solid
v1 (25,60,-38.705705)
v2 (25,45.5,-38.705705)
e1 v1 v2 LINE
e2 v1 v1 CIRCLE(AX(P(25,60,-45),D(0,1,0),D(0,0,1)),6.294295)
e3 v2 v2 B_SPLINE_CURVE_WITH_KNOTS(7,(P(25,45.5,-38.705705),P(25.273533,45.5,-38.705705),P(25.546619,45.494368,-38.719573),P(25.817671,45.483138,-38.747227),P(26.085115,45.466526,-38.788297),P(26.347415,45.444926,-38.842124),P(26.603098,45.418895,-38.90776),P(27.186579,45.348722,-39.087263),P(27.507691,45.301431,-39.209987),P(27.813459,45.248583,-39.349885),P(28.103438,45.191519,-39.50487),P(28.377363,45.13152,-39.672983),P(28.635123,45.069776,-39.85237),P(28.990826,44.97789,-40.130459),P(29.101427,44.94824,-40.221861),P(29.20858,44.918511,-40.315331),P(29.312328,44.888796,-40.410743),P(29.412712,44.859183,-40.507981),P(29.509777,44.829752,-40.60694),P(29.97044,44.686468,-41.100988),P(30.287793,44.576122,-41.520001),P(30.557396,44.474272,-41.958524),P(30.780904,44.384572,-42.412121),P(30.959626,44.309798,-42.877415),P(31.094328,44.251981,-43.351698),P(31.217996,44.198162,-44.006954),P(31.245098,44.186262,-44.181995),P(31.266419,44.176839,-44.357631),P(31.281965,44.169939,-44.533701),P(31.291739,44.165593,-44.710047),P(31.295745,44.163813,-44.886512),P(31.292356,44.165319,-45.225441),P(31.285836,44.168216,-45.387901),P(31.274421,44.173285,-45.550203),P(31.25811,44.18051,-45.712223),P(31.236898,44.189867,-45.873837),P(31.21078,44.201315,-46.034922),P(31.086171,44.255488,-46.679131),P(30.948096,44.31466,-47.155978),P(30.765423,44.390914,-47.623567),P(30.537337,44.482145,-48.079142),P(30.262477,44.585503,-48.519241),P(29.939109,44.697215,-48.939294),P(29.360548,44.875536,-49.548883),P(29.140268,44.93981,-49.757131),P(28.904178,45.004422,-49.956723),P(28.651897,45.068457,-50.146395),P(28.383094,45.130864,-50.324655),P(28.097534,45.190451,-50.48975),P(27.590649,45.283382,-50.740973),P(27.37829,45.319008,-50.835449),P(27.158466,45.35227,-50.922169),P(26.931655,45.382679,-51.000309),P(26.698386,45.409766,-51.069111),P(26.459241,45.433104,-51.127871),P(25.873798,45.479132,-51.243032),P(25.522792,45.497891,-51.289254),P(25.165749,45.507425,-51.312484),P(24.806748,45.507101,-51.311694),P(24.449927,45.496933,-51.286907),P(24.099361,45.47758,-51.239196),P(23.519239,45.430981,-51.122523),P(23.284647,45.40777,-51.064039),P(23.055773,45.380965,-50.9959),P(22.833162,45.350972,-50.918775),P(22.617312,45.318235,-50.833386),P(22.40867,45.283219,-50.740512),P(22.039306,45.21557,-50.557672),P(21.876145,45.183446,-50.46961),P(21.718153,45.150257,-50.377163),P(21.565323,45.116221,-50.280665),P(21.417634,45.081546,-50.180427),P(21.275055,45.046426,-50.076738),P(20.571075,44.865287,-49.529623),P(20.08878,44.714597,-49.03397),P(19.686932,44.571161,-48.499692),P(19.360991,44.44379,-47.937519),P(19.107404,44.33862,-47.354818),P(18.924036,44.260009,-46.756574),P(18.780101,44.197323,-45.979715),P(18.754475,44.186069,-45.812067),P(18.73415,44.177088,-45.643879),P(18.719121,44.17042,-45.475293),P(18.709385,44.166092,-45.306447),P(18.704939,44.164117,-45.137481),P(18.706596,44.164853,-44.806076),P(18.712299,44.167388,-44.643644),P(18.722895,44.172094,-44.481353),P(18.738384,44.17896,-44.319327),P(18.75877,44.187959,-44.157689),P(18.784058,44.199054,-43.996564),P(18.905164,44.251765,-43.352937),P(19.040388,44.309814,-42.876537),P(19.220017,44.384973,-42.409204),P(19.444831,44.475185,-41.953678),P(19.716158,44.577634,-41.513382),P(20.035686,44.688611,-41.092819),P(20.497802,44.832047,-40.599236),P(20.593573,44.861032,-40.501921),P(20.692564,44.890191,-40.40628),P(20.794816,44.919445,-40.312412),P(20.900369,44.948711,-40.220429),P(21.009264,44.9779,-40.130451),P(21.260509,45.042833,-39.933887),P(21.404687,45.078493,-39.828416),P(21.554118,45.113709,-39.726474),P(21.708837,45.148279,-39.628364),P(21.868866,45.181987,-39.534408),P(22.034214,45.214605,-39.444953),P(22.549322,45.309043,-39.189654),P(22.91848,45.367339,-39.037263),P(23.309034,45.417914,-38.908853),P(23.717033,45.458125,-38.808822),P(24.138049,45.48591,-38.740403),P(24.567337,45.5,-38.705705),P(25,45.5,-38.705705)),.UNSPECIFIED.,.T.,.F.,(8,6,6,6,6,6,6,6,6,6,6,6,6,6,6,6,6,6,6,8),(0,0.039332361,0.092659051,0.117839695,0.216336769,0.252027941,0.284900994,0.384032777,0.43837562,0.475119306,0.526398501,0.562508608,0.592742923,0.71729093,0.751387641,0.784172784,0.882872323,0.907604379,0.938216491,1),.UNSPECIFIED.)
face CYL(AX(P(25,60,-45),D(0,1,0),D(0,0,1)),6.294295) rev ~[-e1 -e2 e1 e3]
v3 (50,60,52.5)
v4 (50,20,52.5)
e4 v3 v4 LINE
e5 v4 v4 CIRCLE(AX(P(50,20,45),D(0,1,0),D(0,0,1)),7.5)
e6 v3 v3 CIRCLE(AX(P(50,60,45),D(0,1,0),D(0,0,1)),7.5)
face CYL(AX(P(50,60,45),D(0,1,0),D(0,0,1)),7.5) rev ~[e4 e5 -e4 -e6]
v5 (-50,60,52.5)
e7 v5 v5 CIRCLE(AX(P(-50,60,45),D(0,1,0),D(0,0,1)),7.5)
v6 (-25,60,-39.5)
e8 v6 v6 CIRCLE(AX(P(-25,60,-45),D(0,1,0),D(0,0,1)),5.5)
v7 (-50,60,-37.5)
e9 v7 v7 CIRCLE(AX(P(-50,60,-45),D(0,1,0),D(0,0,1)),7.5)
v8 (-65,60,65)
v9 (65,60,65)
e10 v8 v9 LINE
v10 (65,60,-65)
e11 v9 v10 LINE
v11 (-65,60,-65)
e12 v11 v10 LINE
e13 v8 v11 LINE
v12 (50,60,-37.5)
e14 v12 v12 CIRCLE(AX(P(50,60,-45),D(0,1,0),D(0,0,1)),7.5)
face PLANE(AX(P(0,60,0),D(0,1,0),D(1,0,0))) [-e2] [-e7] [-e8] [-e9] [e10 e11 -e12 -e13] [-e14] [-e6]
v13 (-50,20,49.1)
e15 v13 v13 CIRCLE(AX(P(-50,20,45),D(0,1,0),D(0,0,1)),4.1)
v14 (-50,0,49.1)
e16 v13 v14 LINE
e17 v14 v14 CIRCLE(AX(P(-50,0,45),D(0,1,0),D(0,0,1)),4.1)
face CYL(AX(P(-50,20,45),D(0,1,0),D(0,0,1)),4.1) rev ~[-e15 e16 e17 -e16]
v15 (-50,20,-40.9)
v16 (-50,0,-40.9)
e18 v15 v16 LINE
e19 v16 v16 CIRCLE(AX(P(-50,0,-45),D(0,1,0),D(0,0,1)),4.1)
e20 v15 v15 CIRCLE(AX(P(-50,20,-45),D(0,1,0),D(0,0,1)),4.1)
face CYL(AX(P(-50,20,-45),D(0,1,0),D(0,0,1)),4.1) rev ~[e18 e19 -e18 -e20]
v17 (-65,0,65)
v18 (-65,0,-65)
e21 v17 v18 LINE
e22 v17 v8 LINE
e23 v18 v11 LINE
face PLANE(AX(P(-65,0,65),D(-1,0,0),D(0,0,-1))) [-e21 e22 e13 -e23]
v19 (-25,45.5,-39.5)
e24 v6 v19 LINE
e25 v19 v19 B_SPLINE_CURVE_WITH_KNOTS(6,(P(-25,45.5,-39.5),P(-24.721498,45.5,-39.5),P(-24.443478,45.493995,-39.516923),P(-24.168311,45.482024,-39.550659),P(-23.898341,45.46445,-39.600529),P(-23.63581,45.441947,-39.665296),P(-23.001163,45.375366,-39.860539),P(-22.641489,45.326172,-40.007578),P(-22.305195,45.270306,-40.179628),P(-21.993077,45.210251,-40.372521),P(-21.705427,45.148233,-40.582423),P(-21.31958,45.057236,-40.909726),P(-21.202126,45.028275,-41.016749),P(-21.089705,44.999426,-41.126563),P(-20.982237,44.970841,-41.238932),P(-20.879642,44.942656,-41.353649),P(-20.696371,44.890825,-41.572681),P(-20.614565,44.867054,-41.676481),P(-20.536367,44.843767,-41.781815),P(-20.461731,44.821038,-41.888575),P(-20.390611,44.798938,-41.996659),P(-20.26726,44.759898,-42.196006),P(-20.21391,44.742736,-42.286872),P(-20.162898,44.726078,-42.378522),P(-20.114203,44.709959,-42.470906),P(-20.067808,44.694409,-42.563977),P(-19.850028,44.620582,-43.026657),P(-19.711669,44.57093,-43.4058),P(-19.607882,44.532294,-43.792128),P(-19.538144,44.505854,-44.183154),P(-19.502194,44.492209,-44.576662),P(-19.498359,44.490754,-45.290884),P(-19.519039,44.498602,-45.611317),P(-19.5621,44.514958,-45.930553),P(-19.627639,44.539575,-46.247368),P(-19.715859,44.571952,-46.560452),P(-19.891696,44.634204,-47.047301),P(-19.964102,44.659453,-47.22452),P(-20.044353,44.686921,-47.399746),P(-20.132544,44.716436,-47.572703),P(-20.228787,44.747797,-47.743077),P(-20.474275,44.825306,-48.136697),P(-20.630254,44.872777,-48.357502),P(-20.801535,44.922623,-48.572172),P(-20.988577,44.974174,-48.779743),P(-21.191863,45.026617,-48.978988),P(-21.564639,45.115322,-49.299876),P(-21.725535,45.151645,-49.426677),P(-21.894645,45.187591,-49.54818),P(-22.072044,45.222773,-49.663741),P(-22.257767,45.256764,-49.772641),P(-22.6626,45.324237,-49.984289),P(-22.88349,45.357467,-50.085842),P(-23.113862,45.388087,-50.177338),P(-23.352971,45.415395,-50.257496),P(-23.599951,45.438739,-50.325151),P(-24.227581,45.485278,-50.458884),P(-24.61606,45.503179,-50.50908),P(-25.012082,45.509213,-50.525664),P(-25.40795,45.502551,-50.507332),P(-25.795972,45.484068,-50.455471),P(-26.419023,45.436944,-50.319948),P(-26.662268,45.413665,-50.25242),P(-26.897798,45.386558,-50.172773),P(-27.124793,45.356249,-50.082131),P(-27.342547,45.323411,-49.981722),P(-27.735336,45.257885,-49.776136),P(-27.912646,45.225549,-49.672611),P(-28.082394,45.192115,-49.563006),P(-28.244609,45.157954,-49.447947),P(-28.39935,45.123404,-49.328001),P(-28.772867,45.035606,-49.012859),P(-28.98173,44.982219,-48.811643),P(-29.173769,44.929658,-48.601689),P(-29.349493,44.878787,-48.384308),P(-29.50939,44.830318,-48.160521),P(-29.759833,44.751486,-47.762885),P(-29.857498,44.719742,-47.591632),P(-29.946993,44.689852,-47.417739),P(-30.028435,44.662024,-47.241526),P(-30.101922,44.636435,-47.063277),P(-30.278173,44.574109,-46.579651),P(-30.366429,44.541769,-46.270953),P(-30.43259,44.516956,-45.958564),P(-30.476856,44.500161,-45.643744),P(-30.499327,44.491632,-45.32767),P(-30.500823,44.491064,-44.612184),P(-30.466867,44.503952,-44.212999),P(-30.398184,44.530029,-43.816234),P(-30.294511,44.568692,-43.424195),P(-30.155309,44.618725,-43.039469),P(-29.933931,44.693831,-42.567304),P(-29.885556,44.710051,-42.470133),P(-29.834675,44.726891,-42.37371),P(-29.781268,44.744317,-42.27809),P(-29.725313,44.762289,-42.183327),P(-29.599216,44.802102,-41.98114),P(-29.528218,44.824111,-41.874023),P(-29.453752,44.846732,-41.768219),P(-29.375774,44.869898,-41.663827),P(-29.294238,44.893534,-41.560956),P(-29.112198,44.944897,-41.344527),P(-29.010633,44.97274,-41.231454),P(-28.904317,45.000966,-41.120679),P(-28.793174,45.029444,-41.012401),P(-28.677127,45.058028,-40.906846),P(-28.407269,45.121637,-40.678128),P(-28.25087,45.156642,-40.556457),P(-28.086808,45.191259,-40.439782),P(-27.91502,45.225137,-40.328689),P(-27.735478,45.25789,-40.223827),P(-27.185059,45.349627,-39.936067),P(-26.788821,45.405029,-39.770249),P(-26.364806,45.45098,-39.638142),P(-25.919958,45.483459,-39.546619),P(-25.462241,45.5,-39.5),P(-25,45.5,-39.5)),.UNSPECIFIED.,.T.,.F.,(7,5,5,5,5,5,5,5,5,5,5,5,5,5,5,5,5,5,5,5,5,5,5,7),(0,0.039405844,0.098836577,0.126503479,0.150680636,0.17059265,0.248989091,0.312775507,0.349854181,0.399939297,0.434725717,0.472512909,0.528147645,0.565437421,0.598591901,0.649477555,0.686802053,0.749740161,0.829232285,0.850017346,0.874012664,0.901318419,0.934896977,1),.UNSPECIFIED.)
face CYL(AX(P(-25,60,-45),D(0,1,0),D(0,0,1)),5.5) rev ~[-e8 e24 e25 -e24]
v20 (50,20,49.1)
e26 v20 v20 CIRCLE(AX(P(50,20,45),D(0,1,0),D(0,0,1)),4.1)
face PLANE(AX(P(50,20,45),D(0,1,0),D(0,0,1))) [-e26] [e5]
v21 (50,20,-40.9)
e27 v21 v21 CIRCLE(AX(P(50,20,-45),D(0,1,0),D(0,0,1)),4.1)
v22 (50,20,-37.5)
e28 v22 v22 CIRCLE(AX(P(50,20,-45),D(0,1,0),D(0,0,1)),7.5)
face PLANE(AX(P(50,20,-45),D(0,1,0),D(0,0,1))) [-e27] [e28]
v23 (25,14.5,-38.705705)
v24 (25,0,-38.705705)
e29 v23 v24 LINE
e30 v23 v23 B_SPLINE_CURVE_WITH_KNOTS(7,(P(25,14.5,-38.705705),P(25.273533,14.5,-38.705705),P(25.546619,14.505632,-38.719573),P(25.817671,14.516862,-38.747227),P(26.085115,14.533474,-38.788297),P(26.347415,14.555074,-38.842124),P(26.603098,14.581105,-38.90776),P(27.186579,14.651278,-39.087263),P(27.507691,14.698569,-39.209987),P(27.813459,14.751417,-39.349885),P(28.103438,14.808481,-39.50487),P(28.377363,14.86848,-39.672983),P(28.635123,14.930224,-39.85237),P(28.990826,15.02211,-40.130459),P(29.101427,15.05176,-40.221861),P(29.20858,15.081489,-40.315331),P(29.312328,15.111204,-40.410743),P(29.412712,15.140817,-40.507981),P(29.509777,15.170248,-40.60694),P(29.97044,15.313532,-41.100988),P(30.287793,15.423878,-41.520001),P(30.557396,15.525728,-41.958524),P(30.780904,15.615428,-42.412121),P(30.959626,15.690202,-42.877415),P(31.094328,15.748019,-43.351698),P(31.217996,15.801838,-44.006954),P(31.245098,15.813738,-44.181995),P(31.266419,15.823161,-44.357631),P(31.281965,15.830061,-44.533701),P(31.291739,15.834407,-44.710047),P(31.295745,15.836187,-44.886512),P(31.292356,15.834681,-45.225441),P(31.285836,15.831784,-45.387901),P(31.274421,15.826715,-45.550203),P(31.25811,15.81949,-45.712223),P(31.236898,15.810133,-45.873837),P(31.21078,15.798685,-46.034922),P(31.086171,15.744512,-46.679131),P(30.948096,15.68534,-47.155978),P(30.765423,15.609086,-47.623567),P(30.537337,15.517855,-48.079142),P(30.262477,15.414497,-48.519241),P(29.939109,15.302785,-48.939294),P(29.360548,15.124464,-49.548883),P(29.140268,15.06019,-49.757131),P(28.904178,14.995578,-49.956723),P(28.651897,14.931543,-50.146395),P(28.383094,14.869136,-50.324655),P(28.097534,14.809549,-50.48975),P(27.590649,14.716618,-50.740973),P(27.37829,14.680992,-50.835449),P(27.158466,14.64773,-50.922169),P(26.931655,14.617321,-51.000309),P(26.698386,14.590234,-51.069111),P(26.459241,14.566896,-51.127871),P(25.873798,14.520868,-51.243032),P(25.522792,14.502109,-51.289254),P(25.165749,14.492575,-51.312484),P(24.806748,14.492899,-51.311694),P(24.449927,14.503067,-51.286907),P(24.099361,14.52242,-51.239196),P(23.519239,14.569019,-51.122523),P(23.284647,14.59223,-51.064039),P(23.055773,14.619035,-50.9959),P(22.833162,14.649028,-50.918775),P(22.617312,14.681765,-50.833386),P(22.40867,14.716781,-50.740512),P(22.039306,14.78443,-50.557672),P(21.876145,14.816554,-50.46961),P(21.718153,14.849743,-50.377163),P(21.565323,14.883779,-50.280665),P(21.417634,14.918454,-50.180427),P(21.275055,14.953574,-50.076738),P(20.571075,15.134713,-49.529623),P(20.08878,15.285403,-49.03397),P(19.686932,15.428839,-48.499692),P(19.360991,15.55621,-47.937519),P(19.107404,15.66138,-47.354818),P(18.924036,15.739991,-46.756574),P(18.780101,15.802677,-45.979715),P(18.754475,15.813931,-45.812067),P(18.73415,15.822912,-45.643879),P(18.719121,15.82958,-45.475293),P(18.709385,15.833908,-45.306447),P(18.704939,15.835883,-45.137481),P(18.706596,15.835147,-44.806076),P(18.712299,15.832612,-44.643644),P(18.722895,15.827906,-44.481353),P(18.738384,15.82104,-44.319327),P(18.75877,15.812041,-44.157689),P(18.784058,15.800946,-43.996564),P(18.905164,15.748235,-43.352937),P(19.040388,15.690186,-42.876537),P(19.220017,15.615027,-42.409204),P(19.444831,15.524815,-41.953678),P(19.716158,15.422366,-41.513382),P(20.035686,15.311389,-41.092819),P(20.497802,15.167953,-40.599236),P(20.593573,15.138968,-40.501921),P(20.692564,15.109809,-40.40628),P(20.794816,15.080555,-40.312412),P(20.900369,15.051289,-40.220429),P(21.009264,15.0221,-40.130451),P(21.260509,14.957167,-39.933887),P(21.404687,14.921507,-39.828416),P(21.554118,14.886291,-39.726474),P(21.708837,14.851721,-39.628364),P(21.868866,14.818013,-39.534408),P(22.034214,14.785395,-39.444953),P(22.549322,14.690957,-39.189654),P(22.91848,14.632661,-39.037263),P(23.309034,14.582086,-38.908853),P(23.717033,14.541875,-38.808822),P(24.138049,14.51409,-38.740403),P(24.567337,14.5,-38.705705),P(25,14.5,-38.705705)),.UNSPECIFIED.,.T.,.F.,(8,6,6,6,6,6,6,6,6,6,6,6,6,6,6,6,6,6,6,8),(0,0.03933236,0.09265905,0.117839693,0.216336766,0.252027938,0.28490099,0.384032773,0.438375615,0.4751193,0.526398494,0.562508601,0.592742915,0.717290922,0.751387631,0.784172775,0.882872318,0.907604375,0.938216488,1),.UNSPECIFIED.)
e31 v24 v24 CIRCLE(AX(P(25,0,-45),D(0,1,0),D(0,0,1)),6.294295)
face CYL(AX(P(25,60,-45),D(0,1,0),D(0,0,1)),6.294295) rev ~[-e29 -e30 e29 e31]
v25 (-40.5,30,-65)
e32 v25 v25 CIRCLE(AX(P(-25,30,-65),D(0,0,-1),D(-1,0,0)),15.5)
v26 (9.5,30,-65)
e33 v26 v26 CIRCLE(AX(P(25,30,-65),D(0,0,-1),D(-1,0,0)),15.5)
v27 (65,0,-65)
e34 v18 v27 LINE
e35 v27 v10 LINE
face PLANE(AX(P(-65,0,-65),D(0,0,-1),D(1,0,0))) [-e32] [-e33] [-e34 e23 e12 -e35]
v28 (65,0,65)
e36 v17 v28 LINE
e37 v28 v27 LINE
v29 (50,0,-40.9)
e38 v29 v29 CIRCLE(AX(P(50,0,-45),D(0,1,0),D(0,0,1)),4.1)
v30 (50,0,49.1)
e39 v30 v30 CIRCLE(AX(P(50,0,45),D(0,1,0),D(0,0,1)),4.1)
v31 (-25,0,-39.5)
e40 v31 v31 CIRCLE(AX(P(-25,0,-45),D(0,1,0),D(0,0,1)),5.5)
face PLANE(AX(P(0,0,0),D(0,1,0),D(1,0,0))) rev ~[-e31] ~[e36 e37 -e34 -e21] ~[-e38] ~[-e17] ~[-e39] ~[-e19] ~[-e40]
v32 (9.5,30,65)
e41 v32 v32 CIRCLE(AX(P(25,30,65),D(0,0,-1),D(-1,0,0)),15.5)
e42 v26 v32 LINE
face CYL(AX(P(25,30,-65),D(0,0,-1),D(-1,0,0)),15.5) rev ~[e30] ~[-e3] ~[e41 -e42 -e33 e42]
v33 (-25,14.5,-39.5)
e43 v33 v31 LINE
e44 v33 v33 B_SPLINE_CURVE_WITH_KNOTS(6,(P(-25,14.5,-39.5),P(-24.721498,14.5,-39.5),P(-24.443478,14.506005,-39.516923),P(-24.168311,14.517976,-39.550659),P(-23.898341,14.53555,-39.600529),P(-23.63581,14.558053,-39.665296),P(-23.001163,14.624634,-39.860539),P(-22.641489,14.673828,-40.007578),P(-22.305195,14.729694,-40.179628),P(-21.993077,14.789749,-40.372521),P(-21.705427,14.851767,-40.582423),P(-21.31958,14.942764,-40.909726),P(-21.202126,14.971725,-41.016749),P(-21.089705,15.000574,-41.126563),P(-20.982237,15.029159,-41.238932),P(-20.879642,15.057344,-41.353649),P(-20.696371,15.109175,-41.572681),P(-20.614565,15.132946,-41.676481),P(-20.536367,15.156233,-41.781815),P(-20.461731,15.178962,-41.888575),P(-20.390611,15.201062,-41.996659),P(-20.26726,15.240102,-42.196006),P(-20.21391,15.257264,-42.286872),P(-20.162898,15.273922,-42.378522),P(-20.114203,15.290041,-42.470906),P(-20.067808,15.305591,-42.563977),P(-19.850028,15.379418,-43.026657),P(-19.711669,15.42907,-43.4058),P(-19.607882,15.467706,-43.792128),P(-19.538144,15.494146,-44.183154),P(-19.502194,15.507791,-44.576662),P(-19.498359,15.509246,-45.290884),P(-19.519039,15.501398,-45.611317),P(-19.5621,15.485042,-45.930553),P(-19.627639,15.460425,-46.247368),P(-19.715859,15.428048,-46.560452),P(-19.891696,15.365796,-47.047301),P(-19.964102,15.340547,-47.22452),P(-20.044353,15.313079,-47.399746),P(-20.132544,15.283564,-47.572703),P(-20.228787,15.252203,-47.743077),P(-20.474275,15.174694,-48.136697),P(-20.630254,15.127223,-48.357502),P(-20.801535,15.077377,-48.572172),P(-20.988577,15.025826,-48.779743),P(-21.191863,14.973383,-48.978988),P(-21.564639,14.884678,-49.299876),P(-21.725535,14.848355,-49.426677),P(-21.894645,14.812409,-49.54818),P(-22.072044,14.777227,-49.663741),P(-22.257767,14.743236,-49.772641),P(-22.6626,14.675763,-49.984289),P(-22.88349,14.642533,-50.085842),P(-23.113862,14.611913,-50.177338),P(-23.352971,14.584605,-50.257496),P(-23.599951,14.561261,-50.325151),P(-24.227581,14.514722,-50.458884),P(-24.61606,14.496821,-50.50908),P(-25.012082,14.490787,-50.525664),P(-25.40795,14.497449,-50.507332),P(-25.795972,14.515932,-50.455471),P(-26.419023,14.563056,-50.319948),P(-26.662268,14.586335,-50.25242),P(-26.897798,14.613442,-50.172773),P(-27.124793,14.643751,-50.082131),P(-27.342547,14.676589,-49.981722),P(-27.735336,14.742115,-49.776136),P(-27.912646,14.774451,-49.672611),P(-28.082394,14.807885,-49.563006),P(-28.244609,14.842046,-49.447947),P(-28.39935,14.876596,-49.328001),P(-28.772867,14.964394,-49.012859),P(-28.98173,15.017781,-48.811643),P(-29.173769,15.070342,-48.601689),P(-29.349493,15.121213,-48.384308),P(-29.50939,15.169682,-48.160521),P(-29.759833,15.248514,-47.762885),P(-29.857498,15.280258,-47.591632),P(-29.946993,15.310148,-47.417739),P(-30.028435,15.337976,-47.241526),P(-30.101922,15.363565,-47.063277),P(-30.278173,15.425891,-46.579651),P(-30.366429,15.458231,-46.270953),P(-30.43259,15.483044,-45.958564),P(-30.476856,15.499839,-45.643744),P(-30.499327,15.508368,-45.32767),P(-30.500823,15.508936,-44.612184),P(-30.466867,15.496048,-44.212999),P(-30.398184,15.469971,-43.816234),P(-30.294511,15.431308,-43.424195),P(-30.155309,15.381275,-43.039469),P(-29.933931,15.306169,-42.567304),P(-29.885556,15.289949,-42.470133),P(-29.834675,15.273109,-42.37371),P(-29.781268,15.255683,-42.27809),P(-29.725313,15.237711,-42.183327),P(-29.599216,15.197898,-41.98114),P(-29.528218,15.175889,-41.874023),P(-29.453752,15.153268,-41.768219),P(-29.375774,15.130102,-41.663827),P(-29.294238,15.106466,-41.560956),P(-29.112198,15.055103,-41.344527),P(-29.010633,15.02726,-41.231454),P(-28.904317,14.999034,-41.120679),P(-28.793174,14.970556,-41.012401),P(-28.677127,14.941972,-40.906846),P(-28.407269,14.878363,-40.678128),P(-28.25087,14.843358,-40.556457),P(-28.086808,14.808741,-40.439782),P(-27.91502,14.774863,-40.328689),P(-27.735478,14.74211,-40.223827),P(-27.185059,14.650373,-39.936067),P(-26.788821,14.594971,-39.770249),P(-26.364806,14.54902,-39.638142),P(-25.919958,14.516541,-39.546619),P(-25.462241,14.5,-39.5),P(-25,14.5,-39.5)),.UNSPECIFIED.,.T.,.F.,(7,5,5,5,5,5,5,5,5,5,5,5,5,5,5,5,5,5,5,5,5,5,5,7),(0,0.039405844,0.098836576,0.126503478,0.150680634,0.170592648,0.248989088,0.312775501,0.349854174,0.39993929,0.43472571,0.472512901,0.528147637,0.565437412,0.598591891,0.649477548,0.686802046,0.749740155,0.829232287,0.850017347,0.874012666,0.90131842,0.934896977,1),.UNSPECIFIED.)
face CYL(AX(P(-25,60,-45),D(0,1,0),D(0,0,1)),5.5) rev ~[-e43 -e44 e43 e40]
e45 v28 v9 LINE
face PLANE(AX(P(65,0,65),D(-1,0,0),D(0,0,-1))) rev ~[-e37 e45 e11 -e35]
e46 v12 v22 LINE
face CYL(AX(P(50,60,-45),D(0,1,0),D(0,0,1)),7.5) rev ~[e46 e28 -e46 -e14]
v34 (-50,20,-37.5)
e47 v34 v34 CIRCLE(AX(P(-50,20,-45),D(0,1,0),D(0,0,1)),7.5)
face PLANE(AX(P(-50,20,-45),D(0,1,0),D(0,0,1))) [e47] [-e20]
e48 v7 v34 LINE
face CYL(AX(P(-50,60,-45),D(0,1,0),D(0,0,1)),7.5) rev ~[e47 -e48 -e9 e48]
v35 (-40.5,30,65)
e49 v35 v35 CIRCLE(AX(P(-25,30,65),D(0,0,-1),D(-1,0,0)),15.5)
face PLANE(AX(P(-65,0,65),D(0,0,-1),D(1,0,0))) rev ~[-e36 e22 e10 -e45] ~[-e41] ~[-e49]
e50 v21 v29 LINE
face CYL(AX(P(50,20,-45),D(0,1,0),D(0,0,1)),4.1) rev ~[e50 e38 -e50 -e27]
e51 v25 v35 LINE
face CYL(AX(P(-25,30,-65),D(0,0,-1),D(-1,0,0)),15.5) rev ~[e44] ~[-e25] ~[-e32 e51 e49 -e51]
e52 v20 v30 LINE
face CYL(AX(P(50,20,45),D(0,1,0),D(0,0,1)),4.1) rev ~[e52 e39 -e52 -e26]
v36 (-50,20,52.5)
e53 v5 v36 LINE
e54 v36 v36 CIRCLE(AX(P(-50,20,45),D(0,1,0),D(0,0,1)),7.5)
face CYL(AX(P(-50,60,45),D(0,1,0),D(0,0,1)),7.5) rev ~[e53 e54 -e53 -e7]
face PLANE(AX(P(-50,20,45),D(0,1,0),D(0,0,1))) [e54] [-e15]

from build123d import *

# Parameters (mm, degrees)
SKETCH1_W           = 130
SKETCH1_H           = 130
BOSS_EXTRUDE1_DEPTH = 60
SKETCH2_R           = 15.5
CUT_EXTRUDE1_DEPTH  = 204
SKETCH3_R           = 7.5
CUT_EXTRUDE2_DEPTH  = 40
SKETCH4_R           = 4.1
CUT_EXTRUDE3_DEPTH  = 40
SKETCH5_R           = 6.294295411
SKETCH5_R_2         = 5.5
CUT_EXTRUDE4_DEPTH  = 104


with BuildPart() as part:
    # Sketch1 → Boss-Extrude1 (new body)
    with BuildSketch(Plane(origin=(0, 0, 0), x_dir=(1, 0, 0), z_dir=(0, 1, 0))):
        Rectangle(SKETCH1_W, SKETCH1_H)
    extrude(amount=BOSS_EXTRUDE1_DEPTH)

    # Sketch2 → Cut-Extrude1 (cut)
    with BuildSketch(Plane(origin=(0, 0, -65), x_dir=(-1, 0, 0), z_dir=(0, 0, -1))):
        with Locations((-25, 30)):
            Circle(SKETCH2_R)
        with Locations((25, 30)):
            Circle(SKETCH2_R)
    extrude(amount=-CUT_EXTRUDE1_DEPTH, mode=Mode.SUBTRACT)

    # Sketch3 → Cut-Extrude2 (cut)
    with BuildSketch(Plane(origin=(0, 60, 0), x_dir=(1, 0, 0), z_dir=(0, 1, 0))):
        with Locations(Location((-50, 45, 0), (0, 0, 270))):
            Circle(SKETCH3_R)
        with Locations(Location((50, 45, 0), (0, 0, 270))):
            Circle(SKETCH3_R)
        with Locations(Location((50, -45, 0), (0, 0, 270))):
            Circle(SKETCH3_R)
        with Locations(Location((-50, -45, 0), (0, 0, 270))):
            Circle(SKETCH3_R)
    extrude(amount=-CUT_EXTRUDE2_DEPTH, mode=Mode.SUBTRACT)

    # Sketch4 → Cut-Extrude3 (cut)
    with BuildSketch(Plane(origin=(0, 20, 0), x_dir=(1, 0, 0), z_dir=(0, 1, 0))):
        with Locations(Location((50, 45, 0), (0, 0, 270))):
            Circle(SKETCH4_R)
        with Locations(Location((-50, 45, 0), (0, 0, 270))):
            Circle(SKETCH4_R)
        with Locations(Location((-50, -45, 0), (0, 0, 270))):
            Circle(SKETCH4_R)
        with Locations(Location((50, -45, 0), (0, 0, 270))):
            Circle(SKETCH4_R)
    extrude(amount=-CUT_EXTRUDE3_DEPTH, mode=Mode.SUBTRACT)

    # Sketch5 → Cut-Extrude4 (cut)
    with BuildSketch(Plane(origin=(0, 60, 0), x_dir=(1, 0, 0), z_dir=(0, 1, 0))):
        with Locations(Location((25, 45, 0), (0, 0, 270))):
            Circle(SKETCH5_R)
        with Locations(Location((-25, 45, 0), (0, 0, 270))):
            Circle(SKETCH5_R_2)
    extrude(amount=-CUT_EXTRUDE4_DEPTH, mode=Mode.SUBTRACT)


solid = part.part
